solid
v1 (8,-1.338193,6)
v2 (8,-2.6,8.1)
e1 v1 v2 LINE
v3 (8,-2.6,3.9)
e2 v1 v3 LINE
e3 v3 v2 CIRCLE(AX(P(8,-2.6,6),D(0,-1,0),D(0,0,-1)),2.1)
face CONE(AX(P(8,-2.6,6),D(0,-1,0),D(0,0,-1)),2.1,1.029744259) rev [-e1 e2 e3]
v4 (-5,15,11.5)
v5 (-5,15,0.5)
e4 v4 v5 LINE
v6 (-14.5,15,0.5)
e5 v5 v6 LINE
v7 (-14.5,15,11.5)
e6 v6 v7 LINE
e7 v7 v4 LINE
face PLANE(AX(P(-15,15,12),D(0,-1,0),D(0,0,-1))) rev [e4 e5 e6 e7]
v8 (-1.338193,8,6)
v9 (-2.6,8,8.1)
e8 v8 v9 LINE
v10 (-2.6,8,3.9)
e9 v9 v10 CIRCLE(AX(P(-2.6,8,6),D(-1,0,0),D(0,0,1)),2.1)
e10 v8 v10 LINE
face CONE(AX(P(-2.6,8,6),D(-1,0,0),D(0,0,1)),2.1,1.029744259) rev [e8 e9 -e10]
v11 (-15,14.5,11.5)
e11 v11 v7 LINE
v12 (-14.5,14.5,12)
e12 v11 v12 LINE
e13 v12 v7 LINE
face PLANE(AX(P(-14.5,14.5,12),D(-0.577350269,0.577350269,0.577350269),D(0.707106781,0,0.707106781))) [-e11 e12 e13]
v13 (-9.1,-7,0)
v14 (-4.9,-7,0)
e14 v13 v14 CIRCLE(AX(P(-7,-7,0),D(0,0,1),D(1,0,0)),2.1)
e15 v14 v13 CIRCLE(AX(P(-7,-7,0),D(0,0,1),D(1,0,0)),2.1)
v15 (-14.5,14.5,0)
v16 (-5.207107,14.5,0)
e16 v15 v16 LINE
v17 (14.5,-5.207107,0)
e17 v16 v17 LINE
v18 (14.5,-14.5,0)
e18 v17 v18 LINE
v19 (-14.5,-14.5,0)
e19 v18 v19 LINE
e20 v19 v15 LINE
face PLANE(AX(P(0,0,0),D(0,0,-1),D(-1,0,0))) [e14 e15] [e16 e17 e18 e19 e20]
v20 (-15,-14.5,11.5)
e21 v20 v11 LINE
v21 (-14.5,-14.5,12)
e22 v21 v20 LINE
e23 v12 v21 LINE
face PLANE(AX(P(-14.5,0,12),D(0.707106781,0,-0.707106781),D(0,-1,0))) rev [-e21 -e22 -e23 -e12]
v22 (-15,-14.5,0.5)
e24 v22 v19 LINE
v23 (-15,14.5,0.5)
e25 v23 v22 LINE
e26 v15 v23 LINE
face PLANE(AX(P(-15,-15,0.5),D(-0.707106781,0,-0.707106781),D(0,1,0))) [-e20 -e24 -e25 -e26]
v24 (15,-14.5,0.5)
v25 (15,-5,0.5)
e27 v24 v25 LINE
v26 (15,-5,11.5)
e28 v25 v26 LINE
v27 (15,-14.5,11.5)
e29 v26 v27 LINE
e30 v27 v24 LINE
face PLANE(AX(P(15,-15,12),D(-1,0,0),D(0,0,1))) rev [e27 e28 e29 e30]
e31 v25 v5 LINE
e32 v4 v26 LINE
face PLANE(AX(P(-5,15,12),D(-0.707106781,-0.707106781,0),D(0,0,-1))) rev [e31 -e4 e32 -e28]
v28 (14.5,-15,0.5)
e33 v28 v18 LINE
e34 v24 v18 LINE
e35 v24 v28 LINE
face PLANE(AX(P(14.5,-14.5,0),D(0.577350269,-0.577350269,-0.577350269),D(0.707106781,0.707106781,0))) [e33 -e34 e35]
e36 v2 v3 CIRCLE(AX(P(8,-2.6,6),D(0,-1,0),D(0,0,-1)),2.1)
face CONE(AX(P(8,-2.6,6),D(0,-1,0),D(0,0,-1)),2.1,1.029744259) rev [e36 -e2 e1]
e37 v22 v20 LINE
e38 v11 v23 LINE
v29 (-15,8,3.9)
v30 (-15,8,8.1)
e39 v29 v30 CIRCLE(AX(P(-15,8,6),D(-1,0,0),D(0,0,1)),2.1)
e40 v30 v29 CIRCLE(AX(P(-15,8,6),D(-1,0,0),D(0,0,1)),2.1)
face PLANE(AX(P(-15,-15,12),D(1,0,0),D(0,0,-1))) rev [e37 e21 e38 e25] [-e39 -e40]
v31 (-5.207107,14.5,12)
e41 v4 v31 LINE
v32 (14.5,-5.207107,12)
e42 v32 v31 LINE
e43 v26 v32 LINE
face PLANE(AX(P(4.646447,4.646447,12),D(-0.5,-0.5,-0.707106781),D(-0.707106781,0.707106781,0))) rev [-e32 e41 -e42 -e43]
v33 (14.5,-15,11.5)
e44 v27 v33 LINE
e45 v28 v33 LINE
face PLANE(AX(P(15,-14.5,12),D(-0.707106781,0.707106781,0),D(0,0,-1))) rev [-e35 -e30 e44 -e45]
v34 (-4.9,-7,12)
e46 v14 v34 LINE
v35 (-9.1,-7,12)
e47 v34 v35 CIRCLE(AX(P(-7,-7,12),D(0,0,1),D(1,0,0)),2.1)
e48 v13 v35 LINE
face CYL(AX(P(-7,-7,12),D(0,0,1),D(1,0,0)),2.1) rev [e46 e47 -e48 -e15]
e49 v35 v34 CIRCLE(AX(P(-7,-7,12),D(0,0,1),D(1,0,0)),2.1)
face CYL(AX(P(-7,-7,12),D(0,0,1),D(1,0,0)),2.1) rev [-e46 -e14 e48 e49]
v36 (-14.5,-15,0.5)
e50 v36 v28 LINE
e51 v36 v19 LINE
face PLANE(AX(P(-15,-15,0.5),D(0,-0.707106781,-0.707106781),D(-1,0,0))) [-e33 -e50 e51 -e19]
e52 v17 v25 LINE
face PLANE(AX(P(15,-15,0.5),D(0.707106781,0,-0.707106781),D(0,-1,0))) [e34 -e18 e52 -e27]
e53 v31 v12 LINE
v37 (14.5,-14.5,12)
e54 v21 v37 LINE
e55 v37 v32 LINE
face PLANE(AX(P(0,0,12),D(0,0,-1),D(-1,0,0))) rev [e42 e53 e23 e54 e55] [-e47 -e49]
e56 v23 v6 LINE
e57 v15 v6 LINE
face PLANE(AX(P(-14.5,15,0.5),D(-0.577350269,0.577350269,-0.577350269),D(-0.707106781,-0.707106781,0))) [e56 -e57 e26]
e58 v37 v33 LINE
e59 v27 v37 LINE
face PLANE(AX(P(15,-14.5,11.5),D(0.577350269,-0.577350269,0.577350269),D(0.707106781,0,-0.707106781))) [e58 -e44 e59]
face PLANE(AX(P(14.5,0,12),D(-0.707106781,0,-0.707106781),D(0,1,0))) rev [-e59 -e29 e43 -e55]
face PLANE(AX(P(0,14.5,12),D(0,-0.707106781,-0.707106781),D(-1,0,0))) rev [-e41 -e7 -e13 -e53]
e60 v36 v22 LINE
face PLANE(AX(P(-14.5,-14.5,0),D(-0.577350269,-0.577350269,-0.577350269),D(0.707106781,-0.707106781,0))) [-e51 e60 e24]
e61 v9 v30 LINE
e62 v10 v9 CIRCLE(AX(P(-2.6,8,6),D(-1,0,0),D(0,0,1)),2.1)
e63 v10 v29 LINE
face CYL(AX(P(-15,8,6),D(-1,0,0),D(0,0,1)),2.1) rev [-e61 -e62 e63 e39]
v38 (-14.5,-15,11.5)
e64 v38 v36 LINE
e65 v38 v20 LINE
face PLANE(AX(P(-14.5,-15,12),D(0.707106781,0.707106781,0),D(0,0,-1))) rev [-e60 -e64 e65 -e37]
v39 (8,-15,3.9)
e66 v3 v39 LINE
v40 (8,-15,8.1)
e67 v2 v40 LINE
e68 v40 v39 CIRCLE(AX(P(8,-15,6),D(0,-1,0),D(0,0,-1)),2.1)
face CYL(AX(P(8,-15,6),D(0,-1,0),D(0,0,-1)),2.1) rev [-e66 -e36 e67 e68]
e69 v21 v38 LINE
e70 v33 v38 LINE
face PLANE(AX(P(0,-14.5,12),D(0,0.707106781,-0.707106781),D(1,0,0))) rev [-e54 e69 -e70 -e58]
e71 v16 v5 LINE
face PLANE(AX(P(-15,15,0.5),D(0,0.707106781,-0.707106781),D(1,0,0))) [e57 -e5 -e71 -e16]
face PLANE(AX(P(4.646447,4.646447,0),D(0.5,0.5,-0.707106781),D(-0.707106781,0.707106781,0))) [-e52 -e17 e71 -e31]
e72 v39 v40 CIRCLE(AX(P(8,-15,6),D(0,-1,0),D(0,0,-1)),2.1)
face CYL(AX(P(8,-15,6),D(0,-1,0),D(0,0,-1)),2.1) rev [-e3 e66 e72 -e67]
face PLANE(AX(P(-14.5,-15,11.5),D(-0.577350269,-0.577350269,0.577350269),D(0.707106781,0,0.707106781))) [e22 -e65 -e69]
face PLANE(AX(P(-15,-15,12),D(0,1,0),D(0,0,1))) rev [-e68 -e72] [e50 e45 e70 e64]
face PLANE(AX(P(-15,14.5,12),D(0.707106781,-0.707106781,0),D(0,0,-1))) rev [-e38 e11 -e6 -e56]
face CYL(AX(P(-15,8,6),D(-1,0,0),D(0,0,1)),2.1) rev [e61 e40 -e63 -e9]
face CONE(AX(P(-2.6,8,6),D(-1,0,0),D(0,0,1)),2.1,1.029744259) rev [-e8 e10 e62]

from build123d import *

# Parameters (mm, degrees)
SKETCH_1_W             = 30
SKETCH_1_H             = 30
EXTRUDE_1_DEPTH        = 12
CHAMFER_1_SIZE         = 20
HOLE_WIZARD_M5_1_D     = 4.2
HOLE_WIZARD_M5_2_D     = 4.2
HOLE_WIZARD_M5_2_DEPTH = 12.4
HOLE_WIZARD_M5_2_TIP   = 1.2618073
HOLE_WIZARD_M5_3_D     = 4.2
HOLE_WIZARD_M5_3_DEPTH = 12.4
HOLE_WIZARD_M5_3_TIP   = 1.2618073
CHAMFER_2_SIZE         = 0.5


with BuildPart() as part:
    # 草图1 → 凸台-拉伸1 (new body)
    with BuildSketch(Plane.XY):
        Rectangle(SKETCH_1_W, SKETCH_1_H)
    extrude(amount=EXTRUDE_1_DEPTH)

    # 倒角1
    chamfer_1_edges = [part.edges().sort_by_distance(p)[0] for p in [
        (15, 15, 6),
    ]]
    chamfer(chamfer_1_edges, length=CHAMFER_1_SIZE)

    # M5 螺纹孔1 (through all)
    with Locations(Plane.XY.offset(12)):
        with Locations((-7, -7)):
            Hole(HOLE_WIZARD_M5_1_D / 2)

    # M5 螺纹孔2
    with Locations(Plane(origin=(0, -15, 0), x_dir=(-1, 0, 0), z_dir=(0, -1, 0))):
        with Locations((-8, -6)):
            Hole(HOLE_WIZARD_M5_2_D / 2, depth=HOLE_WIZARD_M5_2_DEPTH)
            with Locations((0, 0, -(HOLE_WIZARD_M5_2_DEPTH + HOLE_WIZARD_M5_2_TIP / 2))):  # 118° drill point
                Cone(0, HOLE_WIZARD_M5_2_D / 2, HOLE_WIZARD_M5_2_TIP, mode=Mode.SUBTRACT)

    # M5 螺纹孔3
    with Locations(Plane.ZY.offset(15)):
        with Locations((6, 8)):
            Hole(HOLE_WIZARD_M5_3_D / 2, depth=HOLE_WIZARD_M5_3_DEPTH)
            with Locations((0, 0, -(HOLE_WIZARD_M5_3_DEPTH + HOLE_WIZARD_M5_3_TIP / 2))):  # 118° drill point
                Cone(0, HOLE_WIZARD_M5_3_D / 2, HOLE_WIZARD_M5_3_TIP, mode=Mode.SUBTRACT)

    # 倒角2
    chamfer_2_edges = [part.edges().sort_by_distance(p)[0] for p in [
        (-15, 0, 12),
        (-10, 15, 0),
        (-10, 15, 12),
        (5, 5, 0),
        (5, 5, 12),
        (0, -15, 12),
        (15, -10, 12),
        (0, -15, 0),
        (-15, 0, 0),
        (15, -10, 0),
        (15, -15, 6),
        (-15, -15, 6),
        (-15, 15, 6),
    ]]
    chamfer(chamfer_2_edges, length=CHAMFER_2_SIZE)


solid = part.part
